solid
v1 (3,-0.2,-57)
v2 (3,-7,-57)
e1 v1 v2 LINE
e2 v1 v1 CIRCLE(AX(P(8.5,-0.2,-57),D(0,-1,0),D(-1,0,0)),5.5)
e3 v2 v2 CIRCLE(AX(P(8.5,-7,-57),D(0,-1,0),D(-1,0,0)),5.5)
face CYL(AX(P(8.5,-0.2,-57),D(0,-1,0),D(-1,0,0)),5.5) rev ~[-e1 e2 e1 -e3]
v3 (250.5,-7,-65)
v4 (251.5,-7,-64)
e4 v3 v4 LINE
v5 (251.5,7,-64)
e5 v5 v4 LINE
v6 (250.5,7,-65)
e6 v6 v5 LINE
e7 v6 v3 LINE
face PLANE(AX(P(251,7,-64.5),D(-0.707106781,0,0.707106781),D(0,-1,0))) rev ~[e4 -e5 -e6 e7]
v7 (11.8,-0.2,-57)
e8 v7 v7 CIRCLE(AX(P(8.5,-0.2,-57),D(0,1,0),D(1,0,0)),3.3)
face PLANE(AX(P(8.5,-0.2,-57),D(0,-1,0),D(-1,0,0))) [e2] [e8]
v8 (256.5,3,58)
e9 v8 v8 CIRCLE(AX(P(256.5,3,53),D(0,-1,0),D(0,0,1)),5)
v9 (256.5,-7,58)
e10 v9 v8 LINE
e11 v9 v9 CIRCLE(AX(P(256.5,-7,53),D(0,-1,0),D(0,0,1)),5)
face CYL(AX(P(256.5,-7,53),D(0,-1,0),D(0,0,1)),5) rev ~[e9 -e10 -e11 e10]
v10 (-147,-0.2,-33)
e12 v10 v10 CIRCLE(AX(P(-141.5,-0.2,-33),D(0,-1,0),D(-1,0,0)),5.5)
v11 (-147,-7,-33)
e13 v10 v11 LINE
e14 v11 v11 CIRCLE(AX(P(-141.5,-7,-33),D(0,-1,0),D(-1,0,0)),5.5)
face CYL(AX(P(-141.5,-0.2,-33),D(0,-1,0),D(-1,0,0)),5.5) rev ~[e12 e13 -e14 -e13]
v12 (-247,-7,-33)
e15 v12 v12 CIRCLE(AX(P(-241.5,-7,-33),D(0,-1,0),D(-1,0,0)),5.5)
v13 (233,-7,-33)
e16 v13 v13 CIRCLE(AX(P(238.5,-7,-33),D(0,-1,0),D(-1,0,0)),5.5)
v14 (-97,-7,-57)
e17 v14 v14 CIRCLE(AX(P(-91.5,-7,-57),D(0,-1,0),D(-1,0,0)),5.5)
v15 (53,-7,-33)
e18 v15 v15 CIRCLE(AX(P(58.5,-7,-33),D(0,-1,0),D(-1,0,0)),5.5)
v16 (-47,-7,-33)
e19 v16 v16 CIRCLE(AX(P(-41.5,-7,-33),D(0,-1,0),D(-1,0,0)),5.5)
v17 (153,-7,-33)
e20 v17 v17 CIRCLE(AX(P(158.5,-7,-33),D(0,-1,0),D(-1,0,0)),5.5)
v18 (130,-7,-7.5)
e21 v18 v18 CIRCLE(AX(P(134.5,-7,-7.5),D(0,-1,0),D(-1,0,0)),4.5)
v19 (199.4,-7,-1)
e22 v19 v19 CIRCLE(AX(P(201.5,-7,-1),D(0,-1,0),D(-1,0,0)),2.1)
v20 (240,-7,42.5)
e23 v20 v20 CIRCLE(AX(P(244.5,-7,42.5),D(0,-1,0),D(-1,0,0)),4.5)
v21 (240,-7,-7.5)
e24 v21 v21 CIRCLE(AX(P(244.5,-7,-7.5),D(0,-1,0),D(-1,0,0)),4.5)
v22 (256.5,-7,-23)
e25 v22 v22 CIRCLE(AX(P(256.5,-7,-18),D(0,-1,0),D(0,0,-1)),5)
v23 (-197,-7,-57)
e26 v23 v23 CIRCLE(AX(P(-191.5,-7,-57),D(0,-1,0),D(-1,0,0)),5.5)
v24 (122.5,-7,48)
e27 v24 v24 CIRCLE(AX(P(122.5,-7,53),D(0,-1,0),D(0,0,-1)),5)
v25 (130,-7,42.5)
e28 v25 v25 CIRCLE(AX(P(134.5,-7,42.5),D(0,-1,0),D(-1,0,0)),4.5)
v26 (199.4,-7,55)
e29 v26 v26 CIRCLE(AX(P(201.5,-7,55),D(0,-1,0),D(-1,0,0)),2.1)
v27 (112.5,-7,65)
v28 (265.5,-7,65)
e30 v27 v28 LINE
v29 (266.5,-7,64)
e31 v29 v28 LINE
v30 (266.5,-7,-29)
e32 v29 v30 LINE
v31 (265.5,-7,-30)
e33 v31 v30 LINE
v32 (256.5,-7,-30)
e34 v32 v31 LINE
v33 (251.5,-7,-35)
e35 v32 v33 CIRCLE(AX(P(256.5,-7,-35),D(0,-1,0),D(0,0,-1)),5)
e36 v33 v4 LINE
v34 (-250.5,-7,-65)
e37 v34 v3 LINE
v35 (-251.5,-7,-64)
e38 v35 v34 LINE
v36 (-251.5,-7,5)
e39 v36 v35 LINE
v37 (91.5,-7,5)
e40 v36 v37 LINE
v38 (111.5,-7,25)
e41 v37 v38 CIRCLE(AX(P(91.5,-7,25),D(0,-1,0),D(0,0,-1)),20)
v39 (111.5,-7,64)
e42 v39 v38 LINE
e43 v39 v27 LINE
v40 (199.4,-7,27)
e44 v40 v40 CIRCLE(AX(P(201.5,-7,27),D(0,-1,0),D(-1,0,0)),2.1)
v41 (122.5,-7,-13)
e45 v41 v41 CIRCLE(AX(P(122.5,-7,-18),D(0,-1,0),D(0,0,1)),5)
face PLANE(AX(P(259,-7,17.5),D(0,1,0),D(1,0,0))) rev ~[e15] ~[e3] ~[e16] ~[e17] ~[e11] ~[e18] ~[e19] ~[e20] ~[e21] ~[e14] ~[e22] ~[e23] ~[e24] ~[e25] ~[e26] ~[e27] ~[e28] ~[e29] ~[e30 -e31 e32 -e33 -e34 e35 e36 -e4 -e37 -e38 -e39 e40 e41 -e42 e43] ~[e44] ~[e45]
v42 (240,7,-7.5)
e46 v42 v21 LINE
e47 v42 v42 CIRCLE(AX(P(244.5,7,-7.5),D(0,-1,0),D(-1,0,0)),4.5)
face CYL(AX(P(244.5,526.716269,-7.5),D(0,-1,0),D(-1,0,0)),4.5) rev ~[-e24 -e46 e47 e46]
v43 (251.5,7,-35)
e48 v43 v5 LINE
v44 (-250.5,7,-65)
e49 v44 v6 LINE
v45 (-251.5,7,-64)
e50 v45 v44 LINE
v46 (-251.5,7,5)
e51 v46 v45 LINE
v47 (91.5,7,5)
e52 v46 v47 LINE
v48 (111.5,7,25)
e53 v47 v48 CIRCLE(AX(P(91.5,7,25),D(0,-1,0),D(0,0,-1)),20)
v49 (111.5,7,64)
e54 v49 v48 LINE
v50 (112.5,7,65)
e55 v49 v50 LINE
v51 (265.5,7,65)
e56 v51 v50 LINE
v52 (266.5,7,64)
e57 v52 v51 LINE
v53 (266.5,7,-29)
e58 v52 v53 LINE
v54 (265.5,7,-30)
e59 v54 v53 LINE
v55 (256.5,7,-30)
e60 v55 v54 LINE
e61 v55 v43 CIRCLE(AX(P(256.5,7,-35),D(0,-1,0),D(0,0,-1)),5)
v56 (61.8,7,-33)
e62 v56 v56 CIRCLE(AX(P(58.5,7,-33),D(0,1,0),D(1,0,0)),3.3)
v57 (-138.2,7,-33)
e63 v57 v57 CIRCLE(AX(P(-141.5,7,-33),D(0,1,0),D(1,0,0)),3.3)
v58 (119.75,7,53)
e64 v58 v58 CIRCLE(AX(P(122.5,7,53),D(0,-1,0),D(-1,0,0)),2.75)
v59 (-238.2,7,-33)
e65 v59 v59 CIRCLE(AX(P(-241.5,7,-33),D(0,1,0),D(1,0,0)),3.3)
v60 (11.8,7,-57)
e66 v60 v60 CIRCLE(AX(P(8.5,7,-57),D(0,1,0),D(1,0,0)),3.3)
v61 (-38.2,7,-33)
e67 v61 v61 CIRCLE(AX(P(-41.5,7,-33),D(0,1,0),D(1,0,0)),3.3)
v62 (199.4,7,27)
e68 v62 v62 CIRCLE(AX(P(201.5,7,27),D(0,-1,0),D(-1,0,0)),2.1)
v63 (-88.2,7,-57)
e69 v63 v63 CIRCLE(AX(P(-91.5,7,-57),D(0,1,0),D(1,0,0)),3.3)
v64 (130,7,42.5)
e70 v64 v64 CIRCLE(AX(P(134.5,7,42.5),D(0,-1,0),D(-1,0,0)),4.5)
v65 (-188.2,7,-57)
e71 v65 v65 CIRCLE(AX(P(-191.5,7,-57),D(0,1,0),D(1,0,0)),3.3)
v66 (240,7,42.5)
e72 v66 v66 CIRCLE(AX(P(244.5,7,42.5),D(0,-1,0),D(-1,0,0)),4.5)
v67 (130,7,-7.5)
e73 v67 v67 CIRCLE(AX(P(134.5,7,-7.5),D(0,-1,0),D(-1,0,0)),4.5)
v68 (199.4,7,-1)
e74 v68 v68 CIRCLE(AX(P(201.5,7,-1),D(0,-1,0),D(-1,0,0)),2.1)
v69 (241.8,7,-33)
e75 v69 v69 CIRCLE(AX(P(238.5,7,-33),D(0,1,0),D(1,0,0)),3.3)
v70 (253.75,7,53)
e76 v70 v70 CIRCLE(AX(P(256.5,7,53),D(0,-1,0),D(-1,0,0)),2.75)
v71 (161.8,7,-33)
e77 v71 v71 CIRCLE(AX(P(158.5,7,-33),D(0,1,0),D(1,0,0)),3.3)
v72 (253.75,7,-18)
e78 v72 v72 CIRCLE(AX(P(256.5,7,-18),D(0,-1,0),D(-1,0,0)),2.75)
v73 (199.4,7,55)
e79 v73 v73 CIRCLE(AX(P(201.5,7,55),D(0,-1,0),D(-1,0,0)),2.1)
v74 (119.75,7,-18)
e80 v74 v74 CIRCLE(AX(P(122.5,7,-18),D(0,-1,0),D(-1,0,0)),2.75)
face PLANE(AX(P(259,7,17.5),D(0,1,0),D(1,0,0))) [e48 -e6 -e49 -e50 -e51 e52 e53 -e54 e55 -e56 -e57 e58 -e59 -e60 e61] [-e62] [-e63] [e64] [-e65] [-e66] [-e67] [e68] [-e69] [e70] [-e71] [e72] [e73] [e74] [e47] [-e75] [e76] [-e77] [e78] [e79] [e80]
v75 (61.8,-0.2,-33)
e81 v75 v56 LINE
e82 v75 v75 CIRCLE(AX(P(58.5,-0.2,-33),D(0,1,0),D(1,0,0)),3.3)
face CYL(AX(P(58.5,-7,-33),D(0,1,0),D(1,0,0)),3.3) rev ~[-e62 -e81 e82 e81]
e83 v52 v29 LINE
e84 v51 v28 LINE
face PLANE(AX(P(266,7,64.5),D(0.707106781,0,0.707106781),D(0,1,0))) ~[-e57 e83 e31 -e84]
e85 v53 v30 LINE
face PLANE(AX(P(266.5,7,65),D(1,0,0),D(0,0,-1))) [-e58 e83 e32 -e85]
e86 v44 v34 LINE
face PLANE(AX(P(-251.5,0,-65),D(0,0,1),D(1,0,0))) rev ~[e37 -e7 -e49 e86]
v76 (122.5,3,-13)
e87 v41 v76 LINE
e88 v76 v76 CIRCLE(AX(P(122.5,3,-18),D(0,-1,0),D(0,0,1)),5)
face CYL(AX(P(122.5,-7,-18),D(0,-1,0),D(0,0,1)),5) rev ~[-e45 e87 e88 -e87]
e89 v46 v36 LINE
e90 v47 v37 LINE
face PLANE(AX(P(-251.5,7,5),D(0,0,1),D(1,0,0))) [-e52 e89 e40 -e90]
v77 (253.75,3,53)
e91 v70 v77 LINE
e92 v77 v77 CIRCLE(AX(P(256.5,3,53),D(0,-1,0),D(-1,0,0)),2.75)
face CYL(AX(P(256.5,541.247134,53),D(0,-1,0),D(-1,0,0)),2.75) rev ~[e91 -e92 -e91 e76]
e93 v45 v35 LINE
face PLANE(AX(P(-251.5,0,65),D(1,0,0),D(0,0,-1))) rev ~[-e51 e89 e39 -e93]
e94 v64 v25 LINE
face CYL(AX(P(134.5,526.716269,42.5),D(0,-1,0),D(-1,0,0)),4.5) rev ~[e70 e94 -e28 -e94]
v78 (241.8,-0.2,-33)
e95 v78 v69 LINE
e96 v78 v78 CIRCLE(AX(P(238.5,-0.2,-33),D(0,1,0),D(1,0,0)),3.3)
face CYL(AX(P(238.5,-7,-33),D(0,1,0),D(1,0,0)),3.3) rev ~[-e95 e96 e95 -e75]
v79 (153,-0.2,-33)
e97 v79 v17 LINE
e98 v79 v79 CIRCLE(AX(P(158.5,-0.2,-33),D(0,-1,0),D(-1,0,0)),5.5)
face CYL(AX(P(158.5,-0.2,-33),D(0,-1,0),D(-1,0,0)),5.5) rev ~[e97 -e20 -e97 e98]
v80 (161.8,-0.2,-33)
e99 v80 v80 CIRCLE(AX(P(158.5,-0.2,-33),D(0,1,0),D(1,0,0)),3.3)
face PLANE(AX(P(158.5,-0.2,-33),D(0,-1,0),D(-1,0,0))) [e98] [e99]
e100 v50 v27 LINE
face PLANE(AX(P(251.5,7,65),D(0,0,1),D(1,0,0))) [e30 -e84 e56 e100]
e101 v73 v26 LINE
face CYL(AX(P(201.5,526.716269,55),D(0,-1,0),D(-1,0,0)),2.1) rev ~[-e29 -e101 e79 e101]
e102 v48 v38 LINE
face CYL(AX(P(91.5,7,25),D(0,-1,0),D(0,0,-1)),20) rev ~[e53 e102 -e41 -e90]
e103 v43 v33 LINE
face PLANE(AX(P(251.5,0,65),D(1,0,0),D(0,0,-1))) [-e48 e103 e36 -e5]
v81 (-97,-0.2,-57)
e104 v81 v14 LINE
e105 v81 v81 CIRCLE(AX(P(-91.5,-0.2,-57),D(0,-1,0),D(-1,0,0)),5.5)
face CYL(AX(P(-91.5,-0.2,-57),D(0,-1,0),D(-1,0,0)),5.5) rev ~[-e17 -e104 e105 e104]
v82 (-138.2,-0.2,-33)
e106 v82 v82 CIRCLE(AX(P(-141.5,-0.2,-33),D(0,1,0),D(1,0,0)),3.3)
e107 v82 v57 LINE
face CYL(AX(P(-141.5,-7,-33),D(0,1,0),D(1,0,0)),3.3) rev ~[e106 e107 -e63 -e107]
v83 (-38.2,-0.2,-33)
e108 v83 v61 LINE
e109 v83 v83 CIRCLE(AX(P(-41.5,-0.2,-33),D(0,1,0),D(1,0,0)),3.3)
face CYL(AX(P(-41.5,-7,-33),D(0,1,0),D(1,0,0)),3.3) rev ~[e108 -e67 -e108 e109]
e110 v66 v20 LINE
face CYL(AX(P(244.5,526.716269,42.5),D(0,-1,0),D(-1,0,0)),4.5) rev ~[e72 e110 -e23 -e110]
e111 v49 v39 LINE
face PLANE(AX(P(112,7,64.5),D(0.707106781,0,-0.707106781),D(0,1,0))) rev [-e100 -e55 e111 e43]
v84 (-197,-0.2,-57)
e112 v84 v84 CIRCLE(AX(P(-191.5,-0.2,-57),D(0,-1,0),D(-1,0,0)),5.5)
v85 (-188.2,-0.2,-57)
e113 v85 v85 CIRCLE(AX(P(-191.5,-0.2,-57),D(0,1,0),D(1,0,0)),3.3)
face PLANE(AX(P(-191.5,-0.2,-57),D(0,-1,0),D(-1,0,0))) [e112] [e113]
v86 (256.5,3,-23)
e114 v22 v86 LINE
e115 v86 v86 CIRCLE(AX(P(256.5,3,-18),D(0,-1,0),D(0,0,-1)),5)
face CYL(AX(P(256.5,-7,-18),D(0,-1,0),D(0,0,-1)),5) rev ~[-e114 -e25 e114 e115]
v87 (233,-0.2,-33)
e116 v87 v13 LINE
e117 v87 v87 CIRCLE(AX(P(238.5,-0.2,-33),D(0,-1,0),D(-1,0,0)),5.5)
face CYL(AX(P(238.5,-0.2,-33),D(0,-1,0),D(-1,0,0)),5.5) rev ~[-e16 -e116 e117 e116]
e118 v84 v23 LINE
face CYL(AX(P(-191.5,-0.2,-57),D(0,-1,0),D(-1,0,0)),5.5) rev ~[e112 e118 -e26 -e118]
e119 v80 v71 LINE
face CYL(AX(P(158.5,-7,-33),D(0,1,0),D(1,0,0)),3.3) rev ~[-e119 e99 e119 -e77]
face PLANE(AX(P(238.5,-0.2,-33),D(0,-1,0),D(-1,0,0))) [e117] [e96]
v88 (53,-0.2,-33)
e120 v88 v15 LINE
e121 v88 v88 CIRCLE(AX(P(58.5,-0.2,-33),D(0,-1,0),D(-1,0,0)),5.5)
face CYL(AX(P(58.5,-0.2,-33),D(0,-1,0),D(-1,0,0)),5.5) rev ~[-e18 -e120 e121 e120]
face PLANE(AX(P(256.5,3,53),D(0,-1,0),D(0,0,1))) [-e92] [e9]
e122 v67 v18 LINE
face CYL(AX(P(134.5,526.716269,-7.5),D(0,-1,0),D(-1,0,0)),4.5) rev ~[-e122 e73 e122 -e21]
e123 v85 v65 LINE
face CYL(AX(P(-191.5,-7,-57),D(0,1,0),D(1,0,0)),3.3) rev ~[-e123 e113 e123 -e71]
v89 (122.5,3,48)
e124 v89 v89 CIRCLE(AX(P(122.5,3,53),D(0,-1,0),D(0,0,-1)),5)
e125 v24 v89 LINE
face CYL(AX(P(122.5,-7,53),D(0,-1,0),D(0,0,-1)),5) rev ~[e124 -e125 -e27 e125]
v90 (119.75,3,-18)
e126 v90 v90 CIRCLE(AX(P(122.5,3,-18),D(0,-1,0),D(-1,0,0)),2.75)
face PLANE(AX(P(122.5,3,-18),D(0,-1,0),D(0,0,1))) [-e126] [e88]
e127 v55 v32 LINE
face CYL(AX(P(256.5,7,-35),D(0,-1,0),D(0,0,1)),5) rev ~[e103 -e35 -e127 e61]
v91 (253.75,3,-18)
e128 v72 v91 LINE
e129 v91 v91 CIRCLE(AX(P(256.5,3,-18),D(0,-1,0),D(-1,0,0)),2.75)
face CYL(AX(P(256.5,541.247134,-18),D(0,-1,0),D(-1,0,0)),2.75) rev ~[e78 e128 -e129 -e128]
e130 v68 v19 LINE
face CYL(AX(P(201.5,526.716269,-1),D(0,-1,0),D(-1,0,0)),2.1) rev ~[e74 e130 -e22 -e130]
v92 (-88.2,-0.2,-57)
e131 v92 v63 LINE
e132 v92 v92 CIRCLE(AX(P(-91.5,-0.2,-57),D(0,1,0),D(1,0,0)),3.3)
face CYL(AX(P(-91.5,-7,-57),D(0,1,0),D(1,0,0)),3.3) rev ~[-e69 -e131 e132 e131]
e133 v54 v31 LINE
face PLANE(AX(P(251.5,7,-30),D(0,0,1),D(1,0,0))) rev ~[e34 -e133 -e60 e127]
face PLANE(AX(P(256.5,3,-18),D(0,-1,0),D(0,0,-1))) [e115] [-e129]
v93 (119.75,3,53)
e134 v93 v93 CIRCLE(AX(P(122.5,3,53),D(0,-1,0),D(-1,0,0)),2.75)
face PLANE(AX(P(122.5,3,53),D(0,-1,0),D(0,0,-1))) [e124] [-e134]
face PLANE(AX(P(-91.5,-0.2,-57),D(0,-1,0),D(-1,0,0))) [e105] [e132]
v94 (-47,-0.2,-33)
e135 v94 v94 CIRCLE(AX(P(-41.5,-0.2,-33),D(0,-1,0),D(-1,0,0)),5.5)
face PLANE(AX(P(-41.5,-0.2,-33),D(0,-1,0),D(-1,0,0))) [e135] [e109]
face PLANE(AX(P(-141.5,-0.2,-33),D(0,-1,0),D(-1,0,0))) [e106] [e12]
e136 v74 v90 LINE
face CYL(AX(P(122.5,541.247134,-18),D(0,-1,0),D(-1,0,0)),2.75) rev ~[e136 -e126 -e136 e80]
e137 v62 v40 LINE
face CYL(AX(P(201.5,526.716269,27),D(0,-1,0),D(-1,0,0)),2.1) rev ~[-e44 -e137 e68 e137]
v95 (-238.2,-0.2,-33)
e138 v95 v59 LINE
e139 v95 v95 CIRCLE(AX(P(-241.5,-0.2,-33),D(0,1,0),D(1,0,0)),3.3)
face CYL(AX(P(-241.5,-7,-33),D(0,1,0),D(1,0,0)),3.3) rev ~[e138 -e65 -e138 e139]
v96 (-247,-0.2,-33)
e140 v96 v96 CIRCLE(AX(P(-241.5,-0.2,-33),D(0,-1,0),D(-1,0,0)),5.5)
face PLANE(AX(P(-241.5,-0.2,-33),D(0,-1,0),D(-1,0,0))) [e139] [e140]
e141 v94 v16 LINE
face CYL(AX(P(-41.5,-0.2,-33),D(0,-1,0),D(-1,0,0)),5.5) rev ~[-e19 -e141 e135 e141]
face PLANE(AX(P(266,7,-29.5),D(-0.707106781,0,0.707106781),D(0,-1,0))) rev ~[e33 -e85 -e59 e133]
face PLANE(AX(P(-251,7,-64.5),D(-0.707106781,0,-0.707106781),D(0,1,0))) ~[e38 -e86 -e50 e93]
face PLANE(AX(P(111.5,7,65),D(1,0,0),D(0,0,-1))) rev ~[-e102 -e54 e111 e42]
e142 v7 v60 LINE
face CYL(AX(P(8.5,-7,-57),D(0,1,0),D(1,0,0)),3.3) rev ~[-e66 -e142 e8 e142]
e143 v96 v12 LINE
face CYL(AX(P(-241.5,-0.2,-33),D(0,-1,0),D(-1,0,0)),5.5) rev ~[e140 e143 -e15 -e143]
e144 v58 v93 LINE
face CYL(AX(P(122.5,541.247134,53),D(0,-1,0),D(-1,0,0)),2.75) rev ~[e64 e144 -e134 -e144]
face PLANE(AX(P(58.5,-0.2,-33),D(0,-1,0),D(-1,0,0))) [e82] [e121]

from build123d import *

# Parameters (mm, degrees)
SKETCH1_W                                            = 503
SKETCH1_H                                            = 130
BOSS_EXTRUDE1_DEPTH                                  = 7
SKETCH2_W                                            = 363
SKETCH2_H                                            = 60
CUT_EXTRUDE1_DEPTH                                   = 261.140827246
M5_TAPPED_HOLE1_D                                    = 4.2
HOLE_SIZE_PER_SOCKET_HEAD_CAP_SCREW_TYPE_D           = 6.6
HOLE_SIZE_PER_SOCKET_HEAD_CAP_SCREW_TYPE_CBORE_D     = 11
HOLE_SIZE_PER_SOCKET_HEAD_CAP_SCREW_TYPE_CBORE_DEPTH = 6.8
M8_CLEARANCE_HOLE1_D                                 = 9
HOLE_SIZE_PER_SOCKET_HEAD_CAP_SCREW_2_D              = 6.6
HOLE_SIZE_PER_SOCKET_HEAD_CAP_SCREW_2_CBORE_D        = 11
HOLE_SIZE_PER_SOCKET_HEAD_CAP_SCREW_2_CBORE_DEPTH    = 6.8
FILLET2_R                                            = 20
CHAMFER1_SIZE                                        = 1
SKETCH12_W                                           = 15
SKETCH12_H                                           = 95
BOSS_EXTRUDE2_DEPTH                                  = 14
SKETCH13_R                                           = 5
CUT_EXTRUDE2_DEPTH                                   = 10
M5_CLEARANCE_HOLE1_D                                 = 5.5
FILLET3_R                                            = 5
CHAMFER2_SIZE                                        = 1


with BuildPart() as part:
    # Sketch1 → Boss-Extrude1 (new, symmetric)
    with BuildSketch(Plane(origin=(0, 0, 0), x_dir=(1, 0, 0), z_dir=(0, 1, 0))):
        Rectangle(SKETCH1_W, SKETCH1_H)
    extrude(amount=BOSS_EXTRUDE1_DEPTH, both=True)

    # Sketch2 → Cut-Extrude1 (cut, through all)
    with BuildSketch(Plane(origin=(0, 7, 0), x_dir=(1, 0, 0), z_dir=(0, 1, 0))):
        with Locations((-70, -35)):
            Rectangle(SKETCH2_W, SKETCH2_H)
    extrude(amount=-CUT_EXTRUDE1_DEPTH, mode=Mode.SUBTRACT)

    # M5 Tapped Hole1 (through all)
    with Locations(Plane(origin=(0, 7, 0), x_dir=(1, 0, 0), z_dir=(0, 1, 0))):
        with Locations((201.5, -55), (201.5, -27), (201.5, 1)):
            Hole(M5_TAPPED_HOLE1_D / 2)

    # Hole Size per Socket Head Cap Screw Type (through all)
    with Locations(Plane(origin=(0, -7, 0), x_dir=(-1, 0, 0), z_dir=(0, -1, 0))):
        with Locations((-8.5, 57), (191.5, 57), (91.5, 57)):
            CounterBoreHole(HOLE_SIZE_PER_SOCKET_HEAD_CAP_SCREW_TYPE_D / 2, HOLE_SIZE_PER_SOCKET_HEAD_CAP_SCREW_TYPE_CBORE_D / 2, HOLE_SIZE_PER_SOCKET_HEAD_CAP_SCREW_TYPE_CBORE_DEPTH)

    # M8 Clearance Hole1 (through all)
    with Locations(Plane(origin=(0, 7, 0), x_dir=(1, 0, 0), z_dir=(0, 1, 0))):
        with Locations((134.5, 7.5), (244.5, -42.5), (134.5, -42.5), (244.5, 7.5)):
            Hole(M8_CLEARANCE_HOLE1_D / 2)

    # Hole Size per Socket Head Cap Screw  2 (through all)
    with Locations(Plane(origin=(0, -7, 0), x_dir=(-1, 0, 0), z_dir=(0, -1, 0))):
        with Locations((-238.5, 33), (241.5, 33), (141.5, 33), (41.5, 33), (-58.5, 33), (-158.5, 33)):
            CounterBoreHole(HOLE_SIZE_PER_SOCKET_HEAD_CAP_SCREW_2_D / 2, HOLE_SIZE_PER_SOCKET_HEAD_CAP_SCREW_2_CBORE_D / 2, HOLE_SIZE_PER_SOCKET_HEAD_CAP_SCREW_2_CBORE_DEPTH)

    # Fillet2
    fillet2_edges = [part.edges().sort_by_distance(p)[0] for p in [
        (111.5, 0, 5),
    ]]
    fillet(fillet2_edges, radius=FILLET2_R)

    # Chamfer1
    chamfer1_edges = [part.edges().sort_by_distance(p)[0] for p in [
        (111.5, 0, 65),
        (-251.5, 0, -65),
        (251.5, 0, -65),
    ]]
    chamfer(chamfer1_edges, length=CHAMFER1_SIZE)

    # Sketch12 → Boss-Extrude2 (add)
    with BuildSketch(Plane(origin=(0, 7, 0), x_dir=(1, 0, 0), z_dir=(0, 1, 0))):
        with Locations((259, -17.5)):
            Rectangle(SKETCH12_W, SKETCH12_H)
    extrude(amount=-BOSS_EXTRUDE2_DEPTH)

    # Sketch13 → Cut-Extrude2 (cut)
    with BuildSketch(Plane.XZ.offset(7)):
        with Locations(Location((122.5, 53, 0), (0, 0, 270))):
            Circle(SKETCH13_R)
        with Locations(Location((256.5, 53, 0), (0, 0, 90))):
            Circle(SKETCH13_R)
        with Locations(Location((256.5, -18, 0), (0, 0, 270))):
            Circle(SKETCH13_R)
        with Locations(Location((122.5, -18, 0), (0, 0, 90))):
            Circle(SKETCH13_R)
    extrude(amount=-CUT_EXTRUDE2_DEPTH, mode=Mode.SUBTRACT)

    # M5 Clearance Hole1 (through all)
    with Locations(Plane(origin=(0, 7, 0), x_dir=(1, 0, 0), z_dir=(0, 1, 0))):
        with Locations((122.5, 18), (122.5, -53), (256.5, -53), (256.5, 18)):
            Hole(M5_CLEARANCE_HOLE1_D / 2)

    # Fillet3
    fillet3_edges = [part.edges().sort_by_distance(p)[0] for p in [
        (251.5, 0, -30),
    ]]
    fillet(fillet3_edges, radius=FILLET3_R)

    # Chamfer2
    chamfer2_edges = [part.edges().sort_by_distance(p)[0] for p in [
        (266.5, 0, 65),
        (266.5, 0, -30),
    ]]
    chamfer(chamfer2_edges, length=CHAMFER2_SIZE)


solid = part.part
